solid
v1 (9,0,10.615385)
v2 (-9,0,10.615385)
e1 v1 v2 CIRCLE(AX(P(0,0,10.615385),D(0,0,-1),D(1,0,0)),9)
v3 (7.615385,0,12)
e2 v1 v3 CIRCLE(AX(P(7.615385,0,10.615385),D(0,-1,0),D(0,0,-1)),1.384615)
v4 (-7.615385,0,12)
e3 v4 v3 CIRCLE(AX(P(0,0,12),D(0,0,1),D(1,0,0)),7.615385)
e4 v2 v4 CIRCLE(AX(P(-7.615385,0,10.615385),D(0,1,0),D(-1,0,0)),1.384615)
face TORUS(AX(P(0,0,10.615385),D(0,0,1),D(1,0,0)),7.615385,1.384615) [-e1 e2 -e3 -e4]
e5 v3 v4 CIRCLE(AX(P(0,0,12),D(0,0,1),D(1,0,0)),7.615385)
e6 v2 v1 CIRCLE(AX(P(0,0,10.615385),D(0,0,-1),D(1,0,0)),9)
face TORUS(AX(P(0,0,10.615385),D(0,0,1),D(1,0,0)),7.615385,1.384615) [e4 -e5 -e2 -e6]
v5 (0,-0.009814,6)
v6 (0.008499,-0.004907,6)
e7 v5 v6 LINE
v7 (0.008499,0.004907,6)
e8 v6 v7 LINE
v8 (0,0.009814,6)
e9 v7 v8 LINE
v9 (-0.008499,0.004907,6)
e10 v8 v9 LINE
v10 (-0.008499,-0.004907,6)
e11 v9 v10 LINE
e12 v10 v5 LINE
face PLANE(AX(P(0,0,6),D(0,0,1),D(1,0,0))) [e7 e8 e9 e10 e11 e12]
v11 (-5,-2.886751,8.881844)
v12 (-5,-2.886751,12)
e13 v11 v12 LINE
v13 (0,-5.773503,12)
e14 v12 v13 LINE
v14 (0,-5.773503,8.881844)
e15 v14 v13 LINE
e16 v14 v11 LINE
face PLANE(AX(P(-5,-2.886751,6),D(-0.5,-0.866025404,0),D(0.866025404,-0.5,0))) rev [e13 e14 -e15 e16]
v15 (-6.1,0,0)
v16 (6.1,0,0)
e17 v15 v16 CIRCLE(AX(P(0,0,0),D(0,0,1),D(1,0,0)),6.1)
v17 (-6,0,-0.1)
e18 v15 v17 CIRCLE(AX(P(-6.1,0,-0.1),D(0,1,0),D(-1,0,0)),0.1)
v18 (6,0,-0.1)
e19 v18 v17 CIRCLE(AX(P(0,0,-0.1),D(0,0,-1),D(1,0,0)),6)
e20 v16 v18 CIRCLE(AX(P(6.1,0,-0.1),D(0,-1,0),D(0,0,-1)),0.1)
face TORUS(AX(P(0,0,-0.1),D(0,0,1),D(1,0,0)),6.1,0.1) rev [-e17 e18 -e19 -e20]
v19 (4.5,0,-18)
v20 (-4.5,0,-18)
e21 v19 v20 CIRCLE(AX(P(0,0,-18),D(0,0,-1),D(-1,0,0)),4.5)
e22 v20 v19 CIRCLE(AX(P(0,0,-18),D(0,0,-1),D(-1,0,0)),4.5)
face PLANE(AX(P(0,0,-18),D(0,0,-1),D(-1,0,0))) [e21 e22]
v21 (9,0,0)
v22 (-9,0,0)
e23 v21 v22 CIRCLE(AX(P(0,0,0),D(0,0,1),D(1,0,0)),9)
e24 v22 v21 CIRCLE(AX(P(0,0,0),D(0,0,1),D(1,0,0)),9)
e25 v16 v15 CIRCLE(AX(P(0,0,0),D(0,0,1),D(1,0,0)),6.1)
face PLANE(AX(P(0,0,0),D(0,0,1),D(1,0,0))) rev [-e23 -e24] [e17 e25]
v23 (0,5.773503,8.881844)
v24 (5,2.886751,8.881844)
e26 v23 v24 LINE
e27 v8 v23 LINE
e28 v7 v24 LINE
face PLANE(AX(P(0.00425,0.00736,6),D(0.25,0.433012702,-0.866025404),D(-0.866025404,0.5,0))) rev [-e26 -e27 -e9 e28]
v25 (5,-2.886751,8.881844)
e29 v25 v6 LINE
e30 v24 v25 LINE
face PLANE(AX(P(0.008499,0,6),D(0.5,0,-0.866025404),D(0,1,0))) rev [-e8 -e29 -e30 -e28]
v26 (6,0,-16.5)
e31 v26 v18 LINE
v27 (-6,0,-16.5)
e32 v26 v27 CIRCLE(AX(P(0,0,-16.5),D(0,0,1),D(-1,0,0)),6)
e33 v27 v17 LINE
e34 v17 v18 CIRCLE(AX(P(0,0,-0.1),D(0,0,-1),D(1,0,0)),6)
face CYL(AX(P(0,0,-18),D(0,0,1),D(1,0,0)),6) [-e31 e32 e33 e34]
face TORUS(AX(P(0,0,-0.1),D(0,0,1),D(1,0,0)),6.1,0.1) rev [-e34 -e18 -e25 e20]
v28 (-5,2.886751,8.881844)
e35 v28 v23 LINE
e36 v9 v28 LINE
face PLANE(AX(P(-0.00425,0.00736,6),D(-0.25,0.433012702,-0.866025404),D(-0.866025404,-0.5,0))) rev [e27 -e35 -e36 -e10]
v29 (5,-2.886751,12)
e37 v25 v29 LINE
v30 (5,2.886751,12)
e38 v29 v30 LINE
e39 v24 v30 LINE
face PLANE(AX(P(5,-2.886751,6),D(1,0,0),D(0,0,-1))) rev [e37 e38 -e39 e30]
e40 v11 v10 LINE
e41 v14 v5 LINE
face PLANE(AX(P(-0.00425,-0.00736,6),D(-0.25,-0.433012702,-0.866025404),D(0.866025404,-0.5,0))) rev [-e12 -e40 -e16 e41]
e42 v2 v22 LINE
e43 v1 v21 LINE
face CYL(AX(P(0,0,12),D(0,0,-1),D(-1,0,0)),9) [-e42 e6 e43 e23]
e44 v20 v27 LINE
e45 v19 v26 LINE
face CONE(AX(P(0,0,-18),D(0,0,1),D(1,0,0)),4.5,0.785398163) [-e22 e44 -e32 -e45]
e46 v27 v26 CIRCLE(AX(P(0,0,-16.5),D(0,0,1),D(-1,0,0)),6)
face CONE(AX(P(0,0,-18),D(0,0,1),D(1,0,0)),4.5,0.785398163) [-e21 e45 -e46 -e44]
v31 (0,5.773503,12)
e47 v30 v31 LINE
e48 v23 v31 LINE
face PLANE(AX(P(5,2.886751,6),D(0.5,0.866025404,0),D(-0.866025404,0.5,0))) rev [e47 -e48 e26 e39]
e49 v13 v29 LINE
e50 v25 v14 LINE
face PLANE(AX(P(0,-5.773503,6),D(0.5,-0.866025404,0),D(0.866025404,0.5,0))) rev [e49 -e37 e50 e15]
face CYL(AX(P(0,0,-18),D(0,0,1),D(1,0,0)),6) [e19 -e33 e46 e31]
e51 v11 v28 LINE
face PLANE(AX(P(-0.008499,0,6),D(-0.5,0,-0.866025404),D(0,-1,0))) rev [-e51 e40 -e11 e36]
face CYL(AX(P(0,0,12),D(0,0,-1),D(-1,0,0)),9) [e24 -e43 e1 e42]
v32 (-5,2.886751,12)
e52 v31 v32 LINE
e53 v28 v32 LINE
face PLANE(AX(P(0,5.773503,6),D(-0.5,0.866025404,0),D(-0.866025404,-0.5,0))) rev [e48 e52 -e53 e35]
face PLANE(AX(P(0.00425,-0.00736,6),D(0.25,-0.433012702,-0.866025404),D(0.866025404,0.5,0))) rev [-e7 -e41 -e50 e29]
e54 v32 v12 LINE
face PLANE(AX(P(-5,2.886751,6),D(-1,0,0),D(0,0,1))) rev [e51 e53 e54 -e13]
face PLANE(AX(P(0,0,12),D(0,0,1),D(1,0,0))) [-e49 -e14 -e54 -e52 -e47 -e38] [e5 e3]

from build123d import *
from OCP.BRepFilletAPI import BRepFilletAPI_MakeChamfer

# Parameters (mm, degrees)
SKETCH1_R           = 9
BOSS_EXTRUDE1_DEPTH = 12
CUT_EXTRUDE1_DEPTH  = 6
SKETCH3_R           = 6
BOSS_EXTRUDE2_DEPTH = 18
CHAMFER1_SIZE       = 1.5
FILLET1_R           = 1.384615385
CHAMFER2_SIZE       = 2.88184438
CHAMFER2_SIZE2      = 4.991500886
FILLET2_R           = 0.1


with BuildPart() as part:
    # Sketch1 → Boss-Extrude1 (new body)
    with BuildSketch(Plane.XY):
        Circle(SKETCH1_R)
    extrude(amount=BOSS_EXTRUDE1_DEPTH)

    # Sketch2 → Cut-Extrude1 (cut)
    with BuildSketch(Plane.XY.offset(12)):
        Polygon((5, 2.886751346), (0, 5.773502692), (-5, 2.886751346), (-5, -2.886751346), (0, -5.773502692), (5, -2.886751346), align=None)
    extrude(amount=-CUT_EXTRUDE1_DEPTH, mode=Mode.SUBTRACT)

    # Sketch3 → Boss-Extrude2 (add)
    with BuildSketch(Plane(origin=(0, 0, 0), x_dir=(-1, 0, 0), z_dir=(0, 0, -1))):
        with Locations(Location((0, 0, 0), (0, 0, 180))):
            Circle(SKETCH3_R)
    extrude(amount=BOSS_EXTRUDE2_DEPTH)

    # Chamfer1
    chamfer1_edges = [part.edges().sort_by_distance(p)[0] for p in [
        (-6, 0, -18),
    ]]
    chamfer(chamfer1_edges, length=CHAMFER1_SIZE)

    # Fillet1
    fillet1_edges = [part.edges().sort_by_distance(p)[0] for p in [
        (-9, 0, 12),
    ]]
    fillet(fillet1_edges, radius=FILLET1_R)

    # Chamfer2: one chamfer whose edges measure the first distance from different faces: ONE call of the kernel's chamfer builder (chamfer() names one face for all edges)
    chamfer2_edges_1 = [part.edges().sort_by_distance(p)[0] for p in [
        (-2.5, 4.330127019, 6),
    ]]
    chamfer2_side_1 = [part.faces().sort_by_distance(p)[0] for p in [
        (-2.5, 4.330127019, 9),
    ]]
    chamfer2_edges_2 = [part.edges().sort_by_distance(p)[0] for p in [
        (2.5, 4.330127019, 6),
    ]]
    chamfer2_side_2 = [part.faces().sort_by_distance(p)[0] for p in [
        (2.5, 4.330127019, 9),
    ]]
    chamfer2_edges_3 = [part.edges().sort_by_distance(p)[0] for p in [
        (5, 0, 6),
    ]]
    chamfer2_side_3 = [part.faces().sort_by_distance(p)[0] for p in [
        (5, 0, 9),
    ]]
    chamfer2_edges_4 = [part.edges().sort_by_distance(p)[0] for p in [
        (2.5, -4.330127019, 6),
    ]]
    chamfer2_side_4 = [part.faces().sort_by_distance(p)[0] for p in [
        (2.5, -4.330127019, 9),
    ]]
    chamfer2_edges_5 = [part.edges().sort_by_distance(p)[0] for p in [
        (-2.5, -4.330127019, 6),
    ]]
    chamfer2_side_5 = [part.faces().sort_by_distance(p)[0] for p in [
        (-2.5, -4.330127019, 9),
    ]]
    chamfer2_edges_6 = [part.edges().sort_by_distance(p)[0] for p in [
        (-5, 0, 6),
    ]]
    chamfer2_side_6 = [part.faces().sort_by_distance(p)[0] for p in [
        (-5, 0, 9),
    ]]
    chamfer2 = BRepFilletAPI_MakeChamfer(part.part.solid().wrapped)
    for e in chamfer2_edges_1:
        chamfer2.Add(CHAMFER2_SIZE, CHAMFER2_SIZE2, e.wrapped, chamfer2_side_1[0].wrapped)  # the first distance lies on this face
    for e in chamfer2_edges_2:
        chamfer2.Add(CHAMFER2_SIZE, CHAMFER2_SIZE2, e.wrapped, chamfer2_side_2[0].wrapped)  # the first distance lies on this face
    for e in chamfer2_edges_3:
        chamfer2.Add(CHAMFER2_SIZE, CHAMFER2_SIZE2, e.wrapped, chamfer2_side_3[0].wrapped)  # the first distance lies on this face
    for e in chamfer2_edges_4:
        chamfer2.Add(CHAMFER2_SIZE, CHAMFER2_SIZE2, e.wrapped, chamfer2_side_4[0].wrapped)  # the first distance lies on this face
    for e in chamfer2_edges_5:
        chamfer2.Add(CHAMFER2_SIZE, CHAMFER2_SIZE2, e.wrapped, chamfer2_side_5[0].wrapped)  # the first distance lies on this face
    for e in chamfer2_edges_6:
        chamfer2.Add(CHAMFER2_SIZE, CHAMFER2_SIZE2, e.wrapped, chamfer2_side_6[0].wrapped)  # the first distance lies on this face
    add(Compound.cast(chamfer2.Shape()), mode=Mode.REPLACE)

    # Fillet2
    fillet2_edges = [part.edges().sort_by_distance(p)[0] for p in [
        (-6, 0, 0),
    ]]
    fillet(fillet2_edges, radius=FILLET2_R)


solid = part.part
